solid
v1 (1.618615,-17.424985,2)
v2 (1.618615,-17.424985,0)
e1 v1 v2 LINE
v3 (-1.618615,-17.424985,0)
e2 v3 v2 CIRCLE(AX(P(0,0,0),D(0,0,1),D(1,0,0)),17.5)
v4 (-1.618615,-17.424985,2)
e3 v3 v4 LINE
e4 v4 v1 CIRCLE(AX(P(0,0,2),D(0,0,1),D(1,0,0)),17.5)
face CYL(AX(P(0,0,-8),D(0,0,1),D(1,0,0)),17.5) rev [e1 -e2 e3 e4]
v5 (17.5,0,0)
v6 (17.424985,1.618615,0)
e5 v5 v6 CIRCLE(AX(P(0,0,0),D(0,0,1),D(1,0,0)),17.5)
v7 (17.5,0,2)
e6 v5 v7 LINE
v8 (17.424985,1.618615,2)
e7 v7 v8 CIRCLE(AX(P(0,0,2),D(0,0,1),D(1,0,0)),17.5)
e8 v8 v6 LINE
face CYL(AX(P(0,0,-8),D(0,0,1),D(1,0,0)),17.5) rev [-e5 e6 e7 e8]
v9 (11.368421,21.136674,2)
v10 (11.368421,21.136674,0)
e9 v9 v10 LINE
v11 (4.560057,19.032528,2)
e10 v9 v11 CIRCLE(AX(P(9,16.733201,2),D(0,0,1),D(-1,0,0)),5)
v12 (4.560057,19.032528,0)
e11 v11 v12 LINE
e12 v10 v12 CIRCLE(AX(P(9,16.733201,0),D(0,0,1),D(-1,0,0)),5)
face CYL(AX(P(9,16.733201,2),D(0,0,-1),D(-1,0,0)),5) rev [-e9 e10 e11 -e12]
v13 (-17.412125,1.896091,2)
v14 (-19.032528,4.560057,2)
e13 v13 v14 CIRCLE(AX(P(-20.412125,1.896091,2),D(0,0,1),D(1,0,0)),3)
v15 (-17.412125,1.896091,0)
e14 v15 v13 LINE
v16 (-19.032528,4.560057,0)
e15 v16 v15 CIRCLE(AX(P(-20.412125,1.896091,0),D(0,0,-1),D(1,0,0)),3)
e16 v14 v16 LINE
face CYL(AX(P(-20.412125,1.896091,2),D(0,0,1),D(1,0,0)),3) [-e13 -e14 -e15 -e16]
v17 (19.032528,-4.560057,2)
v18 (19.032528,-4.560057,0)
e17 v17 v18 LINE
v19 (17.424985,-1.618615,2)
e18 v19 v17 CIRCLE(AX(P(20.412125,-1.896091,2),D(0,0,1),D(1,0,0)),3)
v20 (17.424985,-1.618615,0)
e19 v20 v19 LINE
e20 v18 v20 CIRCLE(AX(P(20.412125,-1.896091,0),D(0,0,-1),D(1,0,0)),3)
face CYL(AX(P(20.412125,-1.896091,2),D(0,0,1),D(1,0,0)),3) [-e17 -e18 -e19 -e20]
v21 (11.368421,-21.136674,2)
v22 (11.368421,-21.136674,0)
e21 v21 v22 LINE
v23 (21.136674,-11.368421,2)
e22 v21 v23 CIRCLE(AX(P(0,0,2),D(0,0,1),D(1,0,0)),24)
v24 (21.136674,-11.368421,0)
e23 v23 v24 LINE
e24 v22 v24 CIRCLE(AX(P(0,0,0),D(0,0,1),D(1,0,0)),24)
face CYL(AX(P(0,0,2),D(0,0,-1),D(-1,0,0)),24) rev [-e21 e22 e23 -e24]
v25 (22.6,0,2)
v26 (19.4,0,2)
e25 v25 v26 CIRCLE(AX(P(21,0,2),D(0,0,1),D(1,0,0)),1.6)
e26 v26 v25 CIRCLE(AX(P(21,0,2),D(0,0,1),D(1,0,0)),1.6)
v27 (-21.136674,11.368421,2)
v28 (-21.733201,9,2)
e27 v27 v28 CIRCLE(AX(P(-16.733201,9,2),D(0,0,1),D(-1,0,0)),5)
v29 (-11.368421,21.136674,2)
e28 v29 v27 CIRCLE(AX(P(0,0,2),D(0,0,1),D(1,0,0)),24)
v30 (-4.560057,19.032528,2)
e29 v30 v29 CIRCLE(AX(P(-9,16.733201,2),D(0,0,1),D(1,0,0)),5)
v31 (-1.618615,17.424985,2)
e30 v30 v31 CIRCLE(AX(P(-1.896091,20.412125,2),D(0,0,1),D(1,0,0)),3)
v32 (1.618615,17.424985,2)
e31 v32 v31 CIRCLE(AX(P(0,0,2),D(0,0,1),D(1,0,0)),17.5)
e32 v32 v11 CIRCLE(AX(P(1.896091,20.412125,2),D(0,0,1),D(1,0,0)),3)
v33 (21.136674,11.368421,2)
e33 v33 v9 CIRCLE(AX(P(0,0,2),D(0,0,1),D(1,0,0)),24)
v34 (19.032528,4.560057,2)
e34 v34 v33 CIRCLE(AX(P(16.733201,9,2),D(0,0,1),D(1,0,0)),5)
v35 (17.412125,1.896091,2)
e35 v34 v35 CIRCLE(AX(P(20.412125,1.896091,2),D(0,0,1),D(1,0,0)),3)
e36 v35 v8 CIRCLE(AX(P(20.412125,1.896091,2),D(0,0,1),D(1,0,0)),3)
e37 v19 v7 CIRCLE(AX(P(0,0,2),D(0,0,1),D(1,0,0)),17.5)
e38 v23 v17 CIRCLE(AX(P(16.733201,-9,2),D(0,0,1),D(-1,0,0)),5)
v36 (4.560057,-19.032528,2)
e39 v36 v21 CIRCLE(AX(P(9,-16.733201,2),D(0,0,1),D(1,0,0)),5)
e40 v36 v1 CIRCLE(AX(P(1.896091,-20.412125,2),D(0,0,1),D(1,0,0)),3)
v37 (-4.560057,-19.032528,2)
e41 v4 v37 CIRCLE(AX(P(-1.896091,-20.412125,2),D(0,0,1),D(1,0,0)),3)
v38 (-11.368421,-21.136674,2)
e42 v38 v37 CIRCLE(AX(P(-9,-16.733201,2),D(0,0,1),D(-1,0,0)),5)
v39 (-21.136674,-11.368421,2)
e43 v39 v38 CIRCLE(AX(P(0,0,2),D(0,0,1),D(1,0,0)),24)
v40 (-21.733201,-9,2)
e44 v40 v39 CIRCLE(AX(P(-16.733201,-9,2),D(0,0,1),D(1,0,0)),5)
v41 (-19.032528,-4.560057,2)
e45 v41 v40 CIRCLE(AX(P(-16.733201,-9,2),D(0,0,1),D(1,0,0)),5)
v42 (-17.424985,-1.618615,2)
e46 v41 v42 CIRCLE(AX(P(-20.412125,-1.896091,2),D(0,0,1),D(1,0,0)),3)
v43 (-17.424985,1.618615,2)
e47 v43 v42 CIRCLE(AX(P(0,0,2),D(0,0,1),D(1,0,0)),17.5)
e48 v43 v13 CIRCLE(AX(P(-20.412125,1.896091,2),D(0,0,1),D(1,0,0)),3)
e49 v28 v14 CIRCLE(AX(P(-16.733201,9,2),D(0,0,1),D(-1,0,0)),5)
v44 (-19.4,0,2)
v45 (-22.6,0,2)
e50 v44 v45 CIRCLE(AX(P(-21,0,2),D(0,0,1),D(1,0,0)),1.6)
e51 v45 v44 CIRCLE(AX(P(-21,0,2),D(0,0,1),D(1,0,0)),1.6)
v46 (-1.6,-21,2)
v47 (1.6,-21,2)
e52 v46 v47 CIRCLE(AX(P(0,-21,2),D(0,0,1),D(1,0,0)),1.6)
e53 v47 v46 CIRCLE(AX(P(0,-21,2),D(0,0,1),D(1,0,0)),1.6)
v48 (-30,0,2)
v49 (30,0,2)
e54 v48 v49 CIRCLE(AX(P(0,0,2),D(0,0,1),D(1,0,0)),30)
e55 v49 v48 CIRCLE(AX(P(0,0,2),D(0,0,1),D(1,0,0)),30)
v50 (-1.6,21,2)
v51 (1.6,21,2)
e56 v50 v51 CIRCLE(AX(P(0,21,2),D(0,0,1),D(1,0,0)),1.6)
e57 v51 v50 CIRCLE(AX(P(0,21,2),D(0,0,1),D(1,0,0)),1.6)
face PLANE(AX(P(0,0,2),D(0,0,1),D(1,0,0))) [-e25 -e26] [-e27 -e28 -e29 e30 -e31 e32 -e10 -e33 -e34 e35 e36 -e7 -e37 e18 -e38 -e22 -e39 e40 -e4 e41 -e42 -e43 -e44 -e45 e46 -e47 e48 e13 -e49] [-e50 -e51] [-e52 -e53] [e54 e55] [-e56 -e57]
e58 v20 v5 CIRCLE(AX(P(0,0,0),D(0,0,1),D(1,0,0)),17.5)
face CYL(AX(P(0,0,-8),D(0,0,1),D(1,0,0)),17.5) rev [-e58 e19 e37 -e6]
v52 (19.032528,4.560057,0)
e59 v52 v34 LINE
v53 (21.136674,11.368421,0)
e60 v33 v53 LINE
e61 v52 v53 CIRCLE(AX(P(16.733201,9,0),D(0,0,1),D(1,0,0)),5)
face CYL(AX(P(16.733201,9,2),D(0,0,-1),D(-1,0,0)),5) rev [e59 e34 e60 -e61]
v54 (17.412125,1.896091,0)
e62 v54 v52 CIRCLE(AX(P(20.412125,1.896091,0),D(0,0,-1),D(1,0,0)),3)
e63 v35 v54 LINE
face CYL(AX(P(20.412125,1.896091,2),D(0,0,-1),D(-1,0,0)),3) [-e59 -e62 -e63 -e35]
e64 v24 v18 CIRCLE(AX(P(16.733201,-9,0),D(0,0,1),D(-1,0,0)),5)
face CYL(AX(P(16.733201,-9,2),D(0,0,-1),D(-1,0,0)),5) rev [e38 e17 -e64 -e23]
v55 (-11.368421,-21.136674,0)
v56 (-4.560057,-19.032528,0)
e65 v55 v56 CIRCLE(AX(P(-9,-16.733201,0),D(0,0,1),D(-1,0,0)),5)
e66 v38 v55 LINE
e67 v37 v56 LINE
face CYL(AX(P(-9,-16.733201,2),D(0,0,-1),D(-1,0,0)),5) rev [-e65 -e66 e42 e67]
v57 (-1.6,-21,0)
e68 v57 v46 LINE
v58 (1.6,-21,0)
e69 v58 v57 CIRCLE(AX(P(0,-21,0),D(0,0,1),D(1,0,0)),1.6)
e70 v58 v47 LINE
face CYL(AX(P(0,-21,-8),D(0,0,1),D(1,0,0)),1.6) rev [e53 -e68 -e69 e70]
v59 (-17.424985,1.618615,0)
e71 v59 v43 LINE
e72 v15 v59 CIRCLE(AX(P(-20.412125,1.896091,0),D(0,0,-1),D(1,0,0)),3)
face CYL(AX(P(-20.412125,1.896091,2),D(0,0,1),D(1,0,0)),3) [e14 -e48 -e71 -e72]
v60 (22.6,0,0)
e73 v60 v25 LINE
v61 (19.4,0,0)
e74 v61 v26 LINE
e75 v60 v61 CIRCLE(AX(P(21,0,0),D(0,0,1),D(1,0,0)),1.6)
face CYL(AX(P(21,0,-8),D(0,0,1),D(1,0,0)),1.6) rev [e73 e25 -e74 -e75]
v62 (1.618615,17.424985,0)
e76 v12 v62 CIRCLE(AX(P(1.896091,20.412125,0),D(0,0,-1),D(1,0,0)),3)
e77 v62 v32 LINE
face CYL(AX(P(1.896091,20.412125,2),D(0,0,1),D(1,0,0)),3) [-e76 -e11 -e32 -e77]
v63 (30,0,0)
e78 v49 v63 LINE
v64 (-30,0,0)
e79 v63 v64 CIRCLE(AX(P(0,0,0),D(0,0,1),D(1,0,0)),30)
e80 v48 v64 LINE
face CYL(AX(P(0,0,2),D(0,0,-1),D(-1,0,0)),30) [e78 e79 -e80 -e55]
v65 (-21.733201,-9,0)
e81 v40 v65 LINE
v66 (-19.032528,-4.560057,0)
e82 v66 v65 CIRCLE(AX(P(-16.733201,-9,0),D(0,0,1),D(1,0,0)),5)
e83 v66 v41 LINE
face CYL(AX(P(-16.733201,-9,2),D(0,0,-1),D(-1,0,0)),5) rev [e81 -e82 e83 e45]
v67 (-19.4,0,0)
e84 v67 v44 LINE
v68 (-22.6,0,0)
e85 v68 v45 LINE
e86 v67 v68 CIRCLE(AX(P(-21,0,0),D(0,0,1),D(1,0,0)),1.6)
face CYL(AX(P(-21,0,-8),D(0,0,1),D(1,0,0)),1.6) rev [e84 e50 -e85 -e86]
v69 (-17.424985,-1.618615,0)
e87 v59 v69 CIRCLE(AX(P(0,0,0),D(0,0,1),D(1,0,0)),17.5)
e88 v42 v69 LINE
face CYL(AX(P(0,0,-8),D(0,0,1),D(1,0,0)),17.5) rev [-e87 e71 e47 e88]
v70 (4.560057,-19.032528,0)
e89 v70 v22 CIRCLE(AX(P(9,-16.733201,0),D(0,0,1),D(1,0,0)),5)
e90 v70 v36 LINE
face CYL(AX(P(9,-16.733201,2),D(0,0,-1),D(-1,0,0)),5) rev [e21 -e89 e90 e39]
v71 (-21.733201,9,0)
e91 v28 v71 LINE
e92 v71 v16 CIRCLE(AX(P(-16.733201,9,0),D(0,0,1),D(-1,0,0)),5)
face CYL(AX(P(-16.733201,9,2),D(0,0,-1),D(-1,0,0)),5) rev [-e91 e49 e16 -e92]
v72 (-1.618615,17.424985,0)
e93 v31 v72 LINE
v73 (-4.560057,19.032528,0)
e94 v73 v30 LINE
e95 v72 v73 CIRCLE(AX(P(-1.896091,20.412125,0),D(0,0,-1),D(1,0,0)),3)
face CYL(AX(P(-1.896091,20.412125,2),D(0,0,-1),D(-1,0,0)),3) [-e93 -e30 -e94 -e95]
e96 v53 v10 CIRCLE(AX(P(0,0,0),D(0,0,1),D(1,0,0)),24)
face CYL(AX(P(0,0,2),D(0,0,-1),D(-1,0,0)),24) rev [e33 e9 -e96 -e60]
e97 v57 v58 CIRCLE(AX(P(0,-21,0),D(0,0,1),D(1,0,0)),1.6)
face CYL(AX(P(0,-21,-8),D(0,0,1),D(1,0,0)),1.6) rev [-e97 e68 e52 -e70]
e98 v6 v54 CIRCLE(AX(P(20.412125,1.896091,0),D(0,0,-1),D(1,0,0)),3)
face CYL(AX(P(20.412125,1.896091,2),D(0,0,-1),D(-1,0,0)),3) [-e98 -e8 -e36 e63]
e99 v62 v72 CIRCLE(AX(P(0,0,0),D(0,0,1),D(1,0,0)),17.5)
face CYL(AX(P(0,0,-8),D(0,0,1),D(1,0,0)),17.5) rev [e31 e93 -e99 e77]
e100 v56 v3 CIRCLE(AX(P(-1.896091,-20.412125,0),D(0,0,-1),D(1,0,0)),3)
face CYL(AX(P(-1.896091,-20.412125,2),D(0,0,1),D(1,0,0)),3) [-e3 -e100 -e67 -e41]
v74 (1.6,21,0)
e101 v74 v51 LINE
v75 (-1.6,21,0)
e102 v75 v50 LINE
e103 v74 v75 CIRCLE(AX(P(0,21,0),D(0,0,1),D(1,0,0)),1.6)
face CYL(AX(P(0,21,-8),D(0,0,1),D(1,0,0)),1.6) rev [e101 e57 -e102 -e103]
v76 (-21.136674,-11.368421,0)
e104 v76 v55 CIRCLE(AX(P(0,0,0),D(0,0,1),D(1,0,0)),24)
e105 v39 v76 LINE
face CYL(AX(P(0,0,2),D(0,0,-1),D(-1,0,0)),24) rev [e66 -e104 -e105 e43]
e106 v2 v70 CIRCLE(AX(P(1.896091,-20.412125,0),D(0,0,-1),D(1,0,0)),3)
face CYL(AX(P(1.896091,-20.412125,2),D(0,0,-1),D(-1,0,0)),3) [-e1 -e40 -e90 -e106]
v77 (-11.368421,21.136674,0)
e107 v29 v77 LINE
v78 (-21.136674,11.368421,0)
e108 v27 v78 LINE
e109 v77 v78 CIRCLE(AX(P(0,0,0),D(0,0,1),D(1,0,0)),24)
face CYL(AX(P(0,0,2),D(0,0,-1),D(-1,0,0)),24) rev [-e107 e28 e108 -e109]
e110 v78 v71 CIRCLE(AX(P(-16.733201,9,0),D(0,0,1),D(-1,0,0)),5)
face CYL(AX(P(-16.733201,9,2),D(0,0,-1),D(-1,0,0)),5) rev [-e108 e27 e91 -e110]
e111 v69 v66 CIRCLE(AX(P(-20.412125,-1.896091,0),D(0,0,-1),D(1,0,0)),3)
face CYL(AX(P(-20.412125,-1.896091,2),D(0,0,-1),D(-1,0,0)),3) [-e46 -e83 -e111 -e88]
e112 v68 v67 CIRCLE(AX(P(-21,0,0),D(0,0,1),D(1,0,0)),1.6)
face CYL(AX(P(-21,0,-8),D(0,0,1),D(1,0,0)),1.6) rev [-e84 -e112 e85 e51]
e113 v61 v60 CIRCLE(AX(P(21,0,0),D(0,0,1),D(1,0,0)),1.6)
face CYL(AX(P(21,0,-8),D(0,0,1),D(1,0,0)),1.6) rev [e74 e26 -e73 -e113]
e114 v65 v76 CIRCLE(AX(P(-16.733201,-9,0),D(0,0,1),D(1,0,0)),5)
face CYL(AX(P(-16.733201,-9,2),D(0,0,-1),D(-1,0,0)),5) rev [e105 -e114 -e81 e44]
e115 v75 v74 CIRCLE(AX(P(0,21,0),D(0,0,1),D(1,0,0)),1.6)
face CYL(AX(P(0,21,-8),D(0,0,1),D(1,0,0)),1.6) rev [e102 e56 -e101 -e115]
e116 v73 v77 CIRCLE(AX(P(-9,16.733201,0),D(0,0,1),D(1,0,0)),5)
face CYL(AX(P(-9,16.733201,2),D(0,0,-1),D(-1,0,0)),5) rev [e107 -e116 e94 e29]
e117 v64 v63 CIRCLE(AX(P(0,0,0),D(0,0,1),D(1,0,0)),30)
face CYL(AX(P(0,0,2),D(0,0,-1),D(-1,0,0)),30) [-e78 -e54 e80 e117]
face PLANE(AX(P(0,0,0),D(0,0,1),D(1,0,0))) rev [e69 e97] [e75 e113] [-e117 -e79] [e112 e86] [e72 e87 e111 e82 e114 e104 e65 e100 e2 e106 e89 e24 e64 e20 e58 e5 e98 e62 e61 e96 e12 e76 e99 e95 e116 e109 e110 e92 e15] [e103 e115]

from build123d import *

# Parameters (mm, degrees)
SKETCH_1_R          = 30
EXTRUDE_1_DEPTH     = 2
SKETCH_2_R          = 1.6
CUT_EXTRUDE_1_DEPTH = 10
SKETCH_3_R          = 2.55
CUT_EXTRUDE_2_DEPTH = 10
SKETCH_4_R          = 17.5
CUT_EXTRUDE_3_DEPTH = 10
FILLET_1_R          = 3


with BuildPart() as part:
    # 草图1 → 凸台-拉伸1 (new body)
    with BuildSketch(Plane.XY):
        Circle(SKETCH_1_R)
        with BuildLine():
            Line((4, 16.733200531), (4, 12))
            ThreePointArc((4, 12), (4.527864045, 9.763932023), (6, 8))
            ThreePointArc((6, 8), (7.071067812, 7.071067812), (8, 6))
            ThreePointArc((8, 6), (9.763932023, 4.527864045), (12, 4))
            Line((12, 4), (16.733200531, 4))
            ThreePointArc((16.733200531, 4), (21.025175907, 6.43505412), (21.136674355, 11.368421053))
            ThreePointArc((21.136674355, 11.368421053), (16.970562748, 16.970562748), (11.368421053, 21.136674355))
            ThreePointArc((11.368421053, 21.136674355), (6.43505412, 21.025175907), (4, 16.733200531))
        make_face(mode=Mode.SUBTRACT)
        with BuildLine():
            Line((-4, 16.733200531), (-4, 12))
            ThreePointArc((-4, 12), (-4.527864045, 9.763932023), (-6, 8))
            ThreePointArc((-6, 8), (-7.071067812, 7.071067812), (-8, 6))
            ThreePointArc((-8, 6), (-9.763932023, 4.527864045), (-12, 4))
            Line((-12, 4), (-16.733200531, 4))
            ThreePointArc((-16.733200531, 4), (-21.025175907, 6.43505412), (-21.136674355, 11.368421053))
            ThreePointArc((-21.136674355, 11.368421053), (-16.970562748, 16.970562748), (-11.368421053, 21.136674355))
            ThreePointArc((-11.368421053, 21.136674355), (-6.43505412, 21.025175907), (-4, 16.733200531))
        make_face(mode=Mode.SUBTRACT)
        with BuildLine():
            Line((16.733200531, -4), (12, -4))
            ThreePointArc((12, -4), (9.763932023, -4.527864045), (8, -6))
            ThreePointArc((8, -6), (7.071067812, -7.071067812), (6, -8))
            ThreePointArc((6, -8), (4.527864045, -9.763932023), (4, -12))
            Line((4, -12), (4, -16.733200531))
            ThreePointArc((4, -16.733200531), (6.43505412, -21.025175907), (11.368421053, -21.136674355))
            ThreePointArc((11.368421053, -21.136674355), (16.970562748, -16.970562748), (21.136674355, -11.368421053))
            ThreePointArc((21.136674355, -11.368421053), (21.025175907, -6.43505412), (16.733200531, -4))
        make_face(mode=Mode.SUBTRACT)
        with BuildLine():
            Line((-4, -16.733200531), (-4, -12))
            ThreePointArc((-4, -12), (-4.527864045, -9.763932023), (-6, -8))
            ThreePointArc((-6, -8), (-7.071067812, -7.071067812), (-8, -6))
            ThreePointArc((-8, -6), (-9.763932023, -4.527864045), (-12, -4))
            Line((-12, -4), (-16.733200531, -4))
            ThreePointArc((-16.733200531, -4), (-21.025175907, -6.43505412), (-21.136674355, -11.368421053))
            ThreePointArc((-21.136674355, -11.368421053), (-16.970562748, -16.970562748), (-11.368421053, -21.136674355))
            ThreePointArc((-11.368421053, -21.136674355), (-6.43505412, -21.025175907), (-4, -16.733200531))
        make_face(mode=Mode.SUBTRACT)
    extrude(amount=EXTRUDE_1_DEPTH)

    # 草图2 → 切除-拉伸1 (cut)
    with BuildSketch(Plane.XY.offset(2)):
        with Locations((-21, 0)):
            Circle(SKETCH_2_R)
        with Locations((0, 21)):
            Circle(SKETCH_2_R)
        with Locations((21, 0)):
            Circle(SKETCH_2_R)
        with Locations((0, -21)):
            Circle(SKETCH_2_R)
    extrude(amount=-CUT_EXTRUDE_1_DEPTH, mode=Mode.SUBTRACT)

    # 草图3 → 切除-拉伸2 (cut)
    with BuildSketch(Plane.XY.offset(2)):
        with Locations((0, 6)):
            Circle(SKETCH_3_R)
        with Locations((-6, 0)):
            Circle(SKETCH_3_R)
        with Locations((6, 0)):
            Circle(SKETCH_3_R)
        with Locations((0, -6)):
            Circle(SKETCH_3_R)
    extrude(amount=-CUT_EXTRUDE_2_DEPTH, mode=Mode.SUBTRACT)

    # 草图4 → 切除-拉伸3 (cut)
    with BuildSketch(Plane.XY.offset(2)):
        Circle(SKETCH_4_R)
    extrude(amount=-CUT_EXTRUDE_3_DEPTH, mode=Mode.SUBTRACT)

    # 圆角1
    fillet_1_edges = [part.edges().sort_by_distance(p)[0] for p in [
        (-4.009091698, -17.034587866, 1),
        (4.009091698, 17.034587866, 1),
        (17.034587866, 4.009091698, 1),
        (17.034587866, -4.009091698, 1),
        (4.009091698, -17.034587866, 1),
        (-17.034587866, -4.009091698, 1),
        (-17.034587866, 4.009091698, 1),
        (-4.009091698, 17.034587866, 1),
    ]]
    fillet(fillet_1_edges, radius=FILLET_1_R)


solid = part.part
